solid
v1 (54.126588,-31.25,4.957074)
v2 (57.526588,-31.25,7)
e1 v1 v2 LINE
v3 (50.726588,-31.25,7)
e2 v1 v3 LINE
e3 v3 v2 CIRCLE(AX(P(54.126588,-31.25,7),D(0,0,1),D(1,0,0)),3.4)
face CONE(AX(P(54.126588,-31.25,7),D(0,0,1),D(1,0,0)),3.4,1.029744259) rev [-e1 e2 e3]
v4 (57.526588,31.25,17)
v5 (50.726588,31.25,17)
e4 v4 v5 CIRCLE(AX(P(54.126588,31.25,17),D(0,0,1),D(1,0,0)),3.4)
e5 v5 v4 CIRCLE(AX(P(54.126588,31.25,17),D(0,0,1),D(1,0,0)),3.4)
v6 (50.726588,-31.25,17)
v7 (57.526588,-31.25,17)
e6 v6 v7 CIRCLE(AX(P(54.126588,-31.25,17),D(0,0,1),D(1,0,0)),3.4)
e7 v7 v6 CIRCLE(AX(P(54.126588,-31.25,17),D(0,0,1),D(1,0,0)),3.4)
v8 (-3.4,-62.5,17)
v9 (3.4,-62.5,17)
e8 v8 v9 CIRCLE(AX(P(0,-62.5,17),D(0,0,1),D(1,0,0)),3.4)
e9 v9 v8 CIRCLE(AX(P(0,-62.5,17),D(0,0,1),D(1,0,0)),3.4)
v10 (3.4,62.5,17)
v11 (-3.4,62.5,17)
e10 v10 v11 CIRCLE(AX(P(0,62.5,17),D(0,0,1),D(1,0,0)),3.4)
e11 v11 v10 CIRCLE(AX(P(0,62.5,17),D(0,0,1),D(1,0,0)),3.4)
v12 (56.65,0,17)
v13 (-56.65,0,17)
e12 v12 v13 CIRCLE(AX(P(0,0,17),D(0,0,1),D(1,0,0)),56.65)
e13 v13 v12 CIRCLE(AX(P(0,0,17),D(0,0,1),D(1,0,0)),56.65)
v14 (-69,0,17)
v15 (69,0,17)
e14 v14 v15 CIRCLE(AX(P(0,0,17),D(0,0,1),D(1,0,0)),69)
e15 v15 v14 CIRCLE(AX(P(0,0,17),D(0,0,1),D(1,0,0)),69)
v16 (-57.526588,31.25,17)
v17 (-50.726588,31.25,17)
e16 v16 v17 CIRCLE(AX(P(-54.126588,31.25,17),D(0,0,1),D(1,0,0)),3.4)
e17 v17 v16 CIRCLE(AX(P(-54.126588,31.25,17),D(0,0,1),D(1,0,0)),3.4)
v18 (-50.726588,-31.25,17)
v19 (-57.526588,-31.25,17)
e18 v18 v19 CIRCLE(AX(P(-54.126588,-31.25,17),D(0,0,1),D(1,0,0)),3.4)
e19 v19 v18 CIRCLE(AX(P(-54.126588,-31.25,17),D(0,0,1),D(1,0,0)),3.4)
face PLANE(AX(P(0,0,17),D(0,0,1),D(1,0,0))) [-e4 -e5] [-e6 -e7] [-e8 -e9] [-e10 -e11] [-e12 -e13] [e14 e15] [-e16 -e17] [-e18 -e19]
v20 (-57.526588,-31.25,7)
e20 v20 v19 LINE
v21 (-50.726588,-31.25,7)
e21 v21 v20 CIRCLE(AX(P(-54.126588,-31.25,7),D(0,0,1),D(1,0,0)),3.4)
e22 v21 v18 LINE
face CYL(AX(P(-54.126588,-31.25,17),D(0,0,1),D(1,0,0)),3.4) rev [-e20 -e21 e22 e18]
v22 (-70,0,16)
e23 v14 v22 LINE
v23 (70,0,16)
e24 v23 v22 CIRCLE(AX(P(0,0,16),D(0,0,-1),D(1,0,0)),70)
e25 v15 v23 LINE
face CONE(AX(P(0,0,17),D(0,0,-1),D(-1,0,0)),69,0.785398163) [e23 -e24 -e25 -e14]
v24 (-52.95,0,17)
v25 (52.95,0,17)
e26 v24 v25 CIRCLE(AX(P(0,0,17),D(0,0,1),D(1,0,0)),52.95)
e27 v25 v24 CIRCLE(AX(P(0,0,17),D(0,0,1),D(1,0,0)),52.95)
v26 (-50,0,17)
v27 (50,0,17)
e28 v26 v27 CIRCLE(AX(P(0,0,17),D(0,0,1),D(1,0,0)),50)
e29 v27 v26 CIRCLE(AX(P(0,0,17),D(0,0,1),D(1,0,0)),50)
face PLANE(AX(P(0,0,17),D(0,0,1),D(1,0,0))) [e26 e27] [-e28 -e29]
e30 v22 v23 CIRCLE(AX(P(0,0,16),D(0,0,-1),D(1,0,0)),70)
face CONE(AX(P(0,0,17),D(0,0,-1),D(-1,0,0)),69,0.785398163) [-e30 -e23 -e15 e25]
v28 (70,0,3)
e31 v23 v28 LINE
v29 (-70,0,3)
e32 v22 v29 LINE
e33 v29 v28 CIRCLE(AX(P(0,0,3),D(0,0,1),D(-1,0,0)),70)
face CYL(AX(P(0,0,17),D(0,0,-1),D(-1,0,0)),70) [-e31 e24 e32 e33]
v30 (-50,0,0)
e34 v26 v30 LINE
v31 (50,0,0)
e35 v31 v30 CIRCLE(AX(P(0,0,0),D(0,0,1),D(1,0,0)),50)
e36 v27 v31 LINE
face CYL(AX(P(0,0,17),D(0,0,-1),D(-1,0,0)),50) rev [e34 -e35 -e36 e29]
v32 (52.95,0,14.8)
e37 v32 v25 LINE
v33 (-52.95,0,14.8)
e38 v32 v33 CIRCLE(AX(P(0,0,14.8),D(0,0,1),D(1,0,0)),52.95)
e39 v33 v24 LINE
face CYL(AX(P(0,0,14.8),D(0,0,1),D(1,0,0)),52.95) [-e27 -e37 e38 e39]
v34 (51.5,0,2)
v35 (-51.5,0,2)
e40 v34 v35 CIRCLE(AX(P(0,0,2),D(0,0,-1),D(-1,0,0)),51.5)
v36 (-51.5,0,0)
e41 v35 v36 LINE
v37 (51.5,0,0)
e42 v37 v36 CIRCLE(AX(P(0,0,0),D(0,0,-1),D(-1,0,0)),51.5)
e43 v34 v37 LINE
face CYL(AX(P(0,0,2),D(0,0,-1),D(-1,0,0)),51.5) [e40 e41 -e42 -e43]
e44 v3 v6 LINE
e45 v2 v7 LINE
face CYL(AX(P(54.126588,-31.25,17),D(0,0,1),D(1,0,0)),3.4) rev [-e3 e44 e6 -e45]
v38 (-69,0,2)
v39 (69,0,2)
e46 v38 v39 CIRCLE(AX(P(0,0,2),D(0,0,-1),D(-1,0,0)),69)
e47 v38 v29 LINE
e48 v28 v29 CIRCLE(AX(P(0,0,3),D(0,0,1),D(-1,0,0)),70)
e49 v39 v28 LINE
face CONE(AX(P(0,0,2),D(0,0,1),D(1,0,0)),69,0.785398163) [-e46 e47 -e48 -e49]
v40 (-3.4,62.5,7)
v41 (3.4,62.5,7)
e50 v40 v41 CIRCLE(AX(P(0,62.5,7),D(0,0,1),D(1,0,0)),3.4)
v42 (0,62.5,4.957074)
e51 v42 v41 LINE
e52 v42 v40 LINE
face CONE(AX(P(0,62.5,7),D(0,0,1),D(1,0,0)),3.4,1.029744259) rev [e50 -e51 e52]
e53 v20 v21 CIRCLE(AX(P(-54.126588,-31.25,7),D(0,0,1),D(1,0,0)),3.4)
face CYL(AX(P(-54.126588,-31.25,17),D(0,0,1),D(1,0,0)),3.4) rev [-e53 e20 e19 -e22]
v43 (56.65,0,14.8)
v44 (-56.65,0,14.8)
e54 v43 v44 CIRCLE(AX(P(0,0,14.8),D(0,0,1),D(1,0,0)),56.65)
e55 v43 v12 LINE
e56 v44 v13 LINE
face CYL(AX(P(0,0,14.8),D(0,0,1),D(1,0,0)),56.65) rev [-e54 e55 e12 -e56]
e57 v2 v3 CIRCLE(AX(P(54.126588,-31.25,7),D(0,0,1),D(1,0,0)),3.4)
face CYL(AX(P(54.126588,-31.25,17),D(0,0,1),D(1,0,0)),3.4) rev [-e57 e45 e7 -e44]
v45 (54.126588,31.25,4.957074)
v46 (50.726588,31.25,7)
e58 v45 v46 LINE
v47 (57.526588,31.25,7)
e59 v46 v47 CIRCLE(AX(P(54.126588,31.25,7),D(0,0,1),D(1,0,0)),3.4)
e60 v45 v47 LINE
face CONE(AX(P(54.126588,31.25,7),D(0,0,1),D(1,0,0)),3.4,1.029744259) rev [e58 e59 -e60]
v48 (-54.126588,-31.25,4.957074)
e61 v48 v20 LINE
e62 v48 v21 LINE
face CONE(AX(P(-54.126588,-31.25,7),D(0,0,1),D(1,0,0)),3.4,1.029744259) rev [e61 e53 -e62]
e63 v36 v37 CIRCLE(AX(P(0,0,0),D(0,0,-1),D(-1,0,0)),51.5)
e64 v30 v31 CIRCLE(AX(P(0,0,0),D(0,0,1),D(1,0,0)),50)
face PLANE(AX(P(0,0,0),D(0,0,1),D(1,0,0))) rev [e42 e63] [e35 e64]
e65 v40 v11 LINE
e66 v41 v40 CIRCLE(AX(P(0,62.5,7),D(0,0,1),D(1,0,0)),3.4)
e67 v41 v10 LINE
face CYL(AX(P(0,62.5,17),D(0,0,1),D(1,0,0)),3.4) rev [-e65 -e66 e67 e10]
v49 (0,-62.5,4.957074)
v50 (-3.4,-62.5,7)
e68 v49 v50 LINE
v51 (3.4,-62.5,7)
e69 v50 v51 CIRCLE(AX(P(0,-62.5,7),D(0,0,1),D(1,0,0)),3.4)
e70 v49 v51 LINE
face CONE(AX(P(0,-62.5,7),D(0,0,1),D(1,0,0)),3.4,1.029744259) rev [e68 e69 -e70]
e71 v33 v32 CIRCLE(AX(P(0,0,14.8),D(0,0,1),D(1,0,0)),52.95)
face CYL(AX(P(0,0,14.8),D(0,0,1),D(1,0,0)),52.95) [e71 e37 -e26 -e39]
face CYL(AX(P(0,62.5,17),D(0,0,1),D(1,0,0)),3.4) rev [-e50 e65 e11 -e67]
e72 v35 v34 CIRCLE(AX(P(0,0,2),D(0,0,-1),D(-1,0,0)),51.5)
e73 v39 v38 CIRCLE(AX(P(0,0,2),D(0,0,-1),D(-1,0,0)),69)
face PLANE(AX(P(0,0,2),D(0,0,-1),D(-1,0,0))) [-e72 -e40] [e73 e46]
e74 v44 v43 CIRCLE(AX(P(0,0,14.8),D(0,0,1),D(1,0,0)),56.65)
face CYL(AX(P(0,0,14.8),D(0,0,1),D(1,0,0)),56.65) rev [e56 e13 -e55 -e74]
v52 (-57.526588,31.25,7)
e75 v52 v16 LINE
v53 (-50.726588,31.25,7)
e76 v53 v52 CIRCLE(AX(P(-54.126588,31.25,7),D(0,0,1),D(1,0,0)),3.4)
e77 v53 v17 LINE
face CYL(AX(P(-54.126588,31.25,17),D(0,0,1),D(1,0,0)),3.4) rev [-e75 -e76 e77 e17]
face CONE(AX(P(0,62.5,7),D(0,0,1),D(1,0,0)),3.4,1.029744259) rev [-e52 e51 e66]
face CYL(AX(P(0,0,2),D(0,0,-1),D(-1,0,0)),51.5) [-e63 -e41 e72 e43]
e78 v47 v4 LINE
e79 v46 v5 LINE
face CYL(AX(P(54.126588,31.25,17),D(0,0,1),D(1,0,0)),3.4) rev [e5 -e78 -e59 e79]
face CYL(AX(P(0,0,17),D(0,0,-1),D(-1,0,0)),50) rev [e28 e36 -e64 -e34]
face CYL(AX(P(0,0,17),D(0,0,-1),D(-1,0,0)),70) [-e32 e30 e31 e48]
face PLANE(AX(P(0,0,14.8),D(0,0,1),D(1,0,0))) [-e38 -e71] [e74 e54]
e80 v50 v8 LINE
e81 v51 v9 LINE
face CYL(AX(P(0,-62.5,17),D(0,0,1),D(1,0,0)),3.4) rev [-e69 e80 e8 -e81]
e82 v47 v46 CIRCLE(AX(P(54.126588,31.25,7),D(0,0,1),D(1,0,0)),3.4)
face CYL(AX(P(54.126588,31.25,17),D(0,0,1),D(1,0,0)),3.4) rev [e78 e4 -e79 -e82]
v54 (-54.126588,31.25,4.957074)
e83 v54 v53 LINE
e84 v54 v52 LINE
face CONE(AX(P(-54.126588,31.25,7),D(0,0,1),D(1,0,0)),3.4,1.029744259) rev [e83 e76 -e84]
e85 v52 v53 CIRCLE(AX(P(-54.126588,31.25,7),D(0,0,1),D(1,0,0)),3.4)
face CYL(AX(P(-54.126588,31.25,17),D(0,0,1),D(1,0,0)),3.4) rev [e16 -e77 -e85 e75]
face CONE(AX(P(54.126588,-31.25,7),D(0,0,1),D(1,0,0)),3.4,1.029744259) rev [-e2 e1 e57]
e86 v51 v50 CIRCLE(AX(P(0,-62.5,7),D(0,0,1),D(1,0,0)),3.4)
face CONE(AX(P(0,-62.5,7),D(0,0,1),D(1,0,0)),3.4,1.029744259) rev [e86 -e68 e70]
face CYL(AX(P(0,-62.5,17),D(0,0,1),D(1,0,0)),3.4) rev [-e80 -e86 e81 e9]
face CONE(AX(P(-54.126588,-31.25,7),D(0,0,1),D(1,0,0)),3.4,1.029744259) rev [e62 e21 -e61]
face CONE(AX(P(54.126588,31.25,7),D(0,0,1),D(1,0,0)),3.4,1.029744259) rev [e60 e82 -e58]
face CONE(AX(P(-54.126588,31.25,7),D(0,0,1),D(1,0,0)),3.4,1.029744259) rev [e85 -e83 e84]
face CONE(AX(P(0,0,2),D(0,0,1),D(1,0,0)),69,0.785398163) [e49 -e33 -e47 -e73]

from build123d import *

# Parameters (mm, degrees)
SKETCH1_R             = 70
SKETCH1_R_2           = 50
BOSS_EXTRUDE1_DEPTH   = 17
SKETCH2_R             = 56.65
SKETCH2_R_2           = 52.95
CUT_EXTRUDE1_DEPTH    = 2.2
SKETCH3_R             = 70
SKETCH3_R_2           = 51.5
CUT_EXTRUDE2_DEPTH    = 2
SKETCH4_R             = 3
CUT_EXTRUDE3_DEPTH    = 10
M8_TAPPED_HOLE1_D     = 6.8
M8_TAPPED_HOLE1_DEPTH = 10
M8_TAPPED_HOLE1_TIP   = 2.042926105
CHAMFER1_SIZE         = 1


with BuildPart() as part:
    # Sketch1 → Boss-Extrude1 (new body)
    with BuildSketch(Plane.XY):
        Circle(SKETCH1_R)
        Circle(SKETCH1_R_2, mode=Mode.SUBTRACT)
    extrude(amount=BOSS_EXTRUDE1_DEPTH)

    # Sketch2 → Cut-Extrude1 (cut)
    with BuildSketch(Plane.XY.offset(17)):
        Circle(SKETCH2_R)
        Circle(SKETCH2_R_2, mode=Mode.SUBTRACT)
    extrude(amount=-CUT_EXTRUDE1_DEPTH, mode=Mode.SUBTRACT)

    # Sketch3 → Cut-Extrude2 (cut)
    with BuildSketch(Plane(origin=(0, 0, 0), x_dir=(-1, 0, 0), z_dir=(0, 0, -1))):
        Circle(SKETCH3_R)
        Circle(SKETCH3_R_2, mode=Mode.SUBTRACT)
    extrude(amount=-CUT_EXTRUDE2_DEPTH, mode=Mode.SUBTRACT)

    # Sketch4 → Cut-Extrude3 (cut)
    with BuildSketch(Plane.XY.offset(17)):
        with Locations((0, 62.5)):
            Circle(SKETCH4_R)
        with Locations((54.126587737, 31.25)):
            Circle(SKETCH4_R)
        with Locations((54.126587737, -31.25)):
            Circle(SKETCH4_R)
        with Locations((0, -62.5)):
            Circle(SKETCH4_R)
        with Locations((-54.126587737, -31.25)):
            Circle(SKETCH4_R)
        with Locations((-54.126587737, 31.25)):
            Circle(SKETCH4_R)
    extrude(amount=-CUT_EXTRUDE3_DEPTH, mode=Mode.SUBTRACT)

    # M8 Tapped Hole1
    with Locations(Plane.XY.offset(17)):
        with Locations((0, 62.5), (54.126587737, 31.25), (54.126587737, -31.25), (0, -62.5), (-54.126587737, -31.25), (-54.126587737, 31.25)):
            Hole(M8_TAPPED_HOLE1_D / 2, depth=M8_TAPPED_HOLE1_DEPTH)
            with Locations((0, 0, -(M8_TAPPED_HOLE1_DEPTH + M8_TAPPED_HOLE1_TIP / 2))):  # 118° drill point
                Cone(0, M8_TAPPED_HOLE1_D / 2, M8_TAPPED_HOLE1_TIP, mode=Mode.SUBTRACT)

    # Chamfer1
    chamfer1_edges = [part.edges().sort_by_distance(p)[0] for p in [
        (-70, 0, 2),
        (-70, 0, 17),
    ]]
    chamfer(chamfer1_edges, length=CHAMFER1_SIZE)


solid = part.part
